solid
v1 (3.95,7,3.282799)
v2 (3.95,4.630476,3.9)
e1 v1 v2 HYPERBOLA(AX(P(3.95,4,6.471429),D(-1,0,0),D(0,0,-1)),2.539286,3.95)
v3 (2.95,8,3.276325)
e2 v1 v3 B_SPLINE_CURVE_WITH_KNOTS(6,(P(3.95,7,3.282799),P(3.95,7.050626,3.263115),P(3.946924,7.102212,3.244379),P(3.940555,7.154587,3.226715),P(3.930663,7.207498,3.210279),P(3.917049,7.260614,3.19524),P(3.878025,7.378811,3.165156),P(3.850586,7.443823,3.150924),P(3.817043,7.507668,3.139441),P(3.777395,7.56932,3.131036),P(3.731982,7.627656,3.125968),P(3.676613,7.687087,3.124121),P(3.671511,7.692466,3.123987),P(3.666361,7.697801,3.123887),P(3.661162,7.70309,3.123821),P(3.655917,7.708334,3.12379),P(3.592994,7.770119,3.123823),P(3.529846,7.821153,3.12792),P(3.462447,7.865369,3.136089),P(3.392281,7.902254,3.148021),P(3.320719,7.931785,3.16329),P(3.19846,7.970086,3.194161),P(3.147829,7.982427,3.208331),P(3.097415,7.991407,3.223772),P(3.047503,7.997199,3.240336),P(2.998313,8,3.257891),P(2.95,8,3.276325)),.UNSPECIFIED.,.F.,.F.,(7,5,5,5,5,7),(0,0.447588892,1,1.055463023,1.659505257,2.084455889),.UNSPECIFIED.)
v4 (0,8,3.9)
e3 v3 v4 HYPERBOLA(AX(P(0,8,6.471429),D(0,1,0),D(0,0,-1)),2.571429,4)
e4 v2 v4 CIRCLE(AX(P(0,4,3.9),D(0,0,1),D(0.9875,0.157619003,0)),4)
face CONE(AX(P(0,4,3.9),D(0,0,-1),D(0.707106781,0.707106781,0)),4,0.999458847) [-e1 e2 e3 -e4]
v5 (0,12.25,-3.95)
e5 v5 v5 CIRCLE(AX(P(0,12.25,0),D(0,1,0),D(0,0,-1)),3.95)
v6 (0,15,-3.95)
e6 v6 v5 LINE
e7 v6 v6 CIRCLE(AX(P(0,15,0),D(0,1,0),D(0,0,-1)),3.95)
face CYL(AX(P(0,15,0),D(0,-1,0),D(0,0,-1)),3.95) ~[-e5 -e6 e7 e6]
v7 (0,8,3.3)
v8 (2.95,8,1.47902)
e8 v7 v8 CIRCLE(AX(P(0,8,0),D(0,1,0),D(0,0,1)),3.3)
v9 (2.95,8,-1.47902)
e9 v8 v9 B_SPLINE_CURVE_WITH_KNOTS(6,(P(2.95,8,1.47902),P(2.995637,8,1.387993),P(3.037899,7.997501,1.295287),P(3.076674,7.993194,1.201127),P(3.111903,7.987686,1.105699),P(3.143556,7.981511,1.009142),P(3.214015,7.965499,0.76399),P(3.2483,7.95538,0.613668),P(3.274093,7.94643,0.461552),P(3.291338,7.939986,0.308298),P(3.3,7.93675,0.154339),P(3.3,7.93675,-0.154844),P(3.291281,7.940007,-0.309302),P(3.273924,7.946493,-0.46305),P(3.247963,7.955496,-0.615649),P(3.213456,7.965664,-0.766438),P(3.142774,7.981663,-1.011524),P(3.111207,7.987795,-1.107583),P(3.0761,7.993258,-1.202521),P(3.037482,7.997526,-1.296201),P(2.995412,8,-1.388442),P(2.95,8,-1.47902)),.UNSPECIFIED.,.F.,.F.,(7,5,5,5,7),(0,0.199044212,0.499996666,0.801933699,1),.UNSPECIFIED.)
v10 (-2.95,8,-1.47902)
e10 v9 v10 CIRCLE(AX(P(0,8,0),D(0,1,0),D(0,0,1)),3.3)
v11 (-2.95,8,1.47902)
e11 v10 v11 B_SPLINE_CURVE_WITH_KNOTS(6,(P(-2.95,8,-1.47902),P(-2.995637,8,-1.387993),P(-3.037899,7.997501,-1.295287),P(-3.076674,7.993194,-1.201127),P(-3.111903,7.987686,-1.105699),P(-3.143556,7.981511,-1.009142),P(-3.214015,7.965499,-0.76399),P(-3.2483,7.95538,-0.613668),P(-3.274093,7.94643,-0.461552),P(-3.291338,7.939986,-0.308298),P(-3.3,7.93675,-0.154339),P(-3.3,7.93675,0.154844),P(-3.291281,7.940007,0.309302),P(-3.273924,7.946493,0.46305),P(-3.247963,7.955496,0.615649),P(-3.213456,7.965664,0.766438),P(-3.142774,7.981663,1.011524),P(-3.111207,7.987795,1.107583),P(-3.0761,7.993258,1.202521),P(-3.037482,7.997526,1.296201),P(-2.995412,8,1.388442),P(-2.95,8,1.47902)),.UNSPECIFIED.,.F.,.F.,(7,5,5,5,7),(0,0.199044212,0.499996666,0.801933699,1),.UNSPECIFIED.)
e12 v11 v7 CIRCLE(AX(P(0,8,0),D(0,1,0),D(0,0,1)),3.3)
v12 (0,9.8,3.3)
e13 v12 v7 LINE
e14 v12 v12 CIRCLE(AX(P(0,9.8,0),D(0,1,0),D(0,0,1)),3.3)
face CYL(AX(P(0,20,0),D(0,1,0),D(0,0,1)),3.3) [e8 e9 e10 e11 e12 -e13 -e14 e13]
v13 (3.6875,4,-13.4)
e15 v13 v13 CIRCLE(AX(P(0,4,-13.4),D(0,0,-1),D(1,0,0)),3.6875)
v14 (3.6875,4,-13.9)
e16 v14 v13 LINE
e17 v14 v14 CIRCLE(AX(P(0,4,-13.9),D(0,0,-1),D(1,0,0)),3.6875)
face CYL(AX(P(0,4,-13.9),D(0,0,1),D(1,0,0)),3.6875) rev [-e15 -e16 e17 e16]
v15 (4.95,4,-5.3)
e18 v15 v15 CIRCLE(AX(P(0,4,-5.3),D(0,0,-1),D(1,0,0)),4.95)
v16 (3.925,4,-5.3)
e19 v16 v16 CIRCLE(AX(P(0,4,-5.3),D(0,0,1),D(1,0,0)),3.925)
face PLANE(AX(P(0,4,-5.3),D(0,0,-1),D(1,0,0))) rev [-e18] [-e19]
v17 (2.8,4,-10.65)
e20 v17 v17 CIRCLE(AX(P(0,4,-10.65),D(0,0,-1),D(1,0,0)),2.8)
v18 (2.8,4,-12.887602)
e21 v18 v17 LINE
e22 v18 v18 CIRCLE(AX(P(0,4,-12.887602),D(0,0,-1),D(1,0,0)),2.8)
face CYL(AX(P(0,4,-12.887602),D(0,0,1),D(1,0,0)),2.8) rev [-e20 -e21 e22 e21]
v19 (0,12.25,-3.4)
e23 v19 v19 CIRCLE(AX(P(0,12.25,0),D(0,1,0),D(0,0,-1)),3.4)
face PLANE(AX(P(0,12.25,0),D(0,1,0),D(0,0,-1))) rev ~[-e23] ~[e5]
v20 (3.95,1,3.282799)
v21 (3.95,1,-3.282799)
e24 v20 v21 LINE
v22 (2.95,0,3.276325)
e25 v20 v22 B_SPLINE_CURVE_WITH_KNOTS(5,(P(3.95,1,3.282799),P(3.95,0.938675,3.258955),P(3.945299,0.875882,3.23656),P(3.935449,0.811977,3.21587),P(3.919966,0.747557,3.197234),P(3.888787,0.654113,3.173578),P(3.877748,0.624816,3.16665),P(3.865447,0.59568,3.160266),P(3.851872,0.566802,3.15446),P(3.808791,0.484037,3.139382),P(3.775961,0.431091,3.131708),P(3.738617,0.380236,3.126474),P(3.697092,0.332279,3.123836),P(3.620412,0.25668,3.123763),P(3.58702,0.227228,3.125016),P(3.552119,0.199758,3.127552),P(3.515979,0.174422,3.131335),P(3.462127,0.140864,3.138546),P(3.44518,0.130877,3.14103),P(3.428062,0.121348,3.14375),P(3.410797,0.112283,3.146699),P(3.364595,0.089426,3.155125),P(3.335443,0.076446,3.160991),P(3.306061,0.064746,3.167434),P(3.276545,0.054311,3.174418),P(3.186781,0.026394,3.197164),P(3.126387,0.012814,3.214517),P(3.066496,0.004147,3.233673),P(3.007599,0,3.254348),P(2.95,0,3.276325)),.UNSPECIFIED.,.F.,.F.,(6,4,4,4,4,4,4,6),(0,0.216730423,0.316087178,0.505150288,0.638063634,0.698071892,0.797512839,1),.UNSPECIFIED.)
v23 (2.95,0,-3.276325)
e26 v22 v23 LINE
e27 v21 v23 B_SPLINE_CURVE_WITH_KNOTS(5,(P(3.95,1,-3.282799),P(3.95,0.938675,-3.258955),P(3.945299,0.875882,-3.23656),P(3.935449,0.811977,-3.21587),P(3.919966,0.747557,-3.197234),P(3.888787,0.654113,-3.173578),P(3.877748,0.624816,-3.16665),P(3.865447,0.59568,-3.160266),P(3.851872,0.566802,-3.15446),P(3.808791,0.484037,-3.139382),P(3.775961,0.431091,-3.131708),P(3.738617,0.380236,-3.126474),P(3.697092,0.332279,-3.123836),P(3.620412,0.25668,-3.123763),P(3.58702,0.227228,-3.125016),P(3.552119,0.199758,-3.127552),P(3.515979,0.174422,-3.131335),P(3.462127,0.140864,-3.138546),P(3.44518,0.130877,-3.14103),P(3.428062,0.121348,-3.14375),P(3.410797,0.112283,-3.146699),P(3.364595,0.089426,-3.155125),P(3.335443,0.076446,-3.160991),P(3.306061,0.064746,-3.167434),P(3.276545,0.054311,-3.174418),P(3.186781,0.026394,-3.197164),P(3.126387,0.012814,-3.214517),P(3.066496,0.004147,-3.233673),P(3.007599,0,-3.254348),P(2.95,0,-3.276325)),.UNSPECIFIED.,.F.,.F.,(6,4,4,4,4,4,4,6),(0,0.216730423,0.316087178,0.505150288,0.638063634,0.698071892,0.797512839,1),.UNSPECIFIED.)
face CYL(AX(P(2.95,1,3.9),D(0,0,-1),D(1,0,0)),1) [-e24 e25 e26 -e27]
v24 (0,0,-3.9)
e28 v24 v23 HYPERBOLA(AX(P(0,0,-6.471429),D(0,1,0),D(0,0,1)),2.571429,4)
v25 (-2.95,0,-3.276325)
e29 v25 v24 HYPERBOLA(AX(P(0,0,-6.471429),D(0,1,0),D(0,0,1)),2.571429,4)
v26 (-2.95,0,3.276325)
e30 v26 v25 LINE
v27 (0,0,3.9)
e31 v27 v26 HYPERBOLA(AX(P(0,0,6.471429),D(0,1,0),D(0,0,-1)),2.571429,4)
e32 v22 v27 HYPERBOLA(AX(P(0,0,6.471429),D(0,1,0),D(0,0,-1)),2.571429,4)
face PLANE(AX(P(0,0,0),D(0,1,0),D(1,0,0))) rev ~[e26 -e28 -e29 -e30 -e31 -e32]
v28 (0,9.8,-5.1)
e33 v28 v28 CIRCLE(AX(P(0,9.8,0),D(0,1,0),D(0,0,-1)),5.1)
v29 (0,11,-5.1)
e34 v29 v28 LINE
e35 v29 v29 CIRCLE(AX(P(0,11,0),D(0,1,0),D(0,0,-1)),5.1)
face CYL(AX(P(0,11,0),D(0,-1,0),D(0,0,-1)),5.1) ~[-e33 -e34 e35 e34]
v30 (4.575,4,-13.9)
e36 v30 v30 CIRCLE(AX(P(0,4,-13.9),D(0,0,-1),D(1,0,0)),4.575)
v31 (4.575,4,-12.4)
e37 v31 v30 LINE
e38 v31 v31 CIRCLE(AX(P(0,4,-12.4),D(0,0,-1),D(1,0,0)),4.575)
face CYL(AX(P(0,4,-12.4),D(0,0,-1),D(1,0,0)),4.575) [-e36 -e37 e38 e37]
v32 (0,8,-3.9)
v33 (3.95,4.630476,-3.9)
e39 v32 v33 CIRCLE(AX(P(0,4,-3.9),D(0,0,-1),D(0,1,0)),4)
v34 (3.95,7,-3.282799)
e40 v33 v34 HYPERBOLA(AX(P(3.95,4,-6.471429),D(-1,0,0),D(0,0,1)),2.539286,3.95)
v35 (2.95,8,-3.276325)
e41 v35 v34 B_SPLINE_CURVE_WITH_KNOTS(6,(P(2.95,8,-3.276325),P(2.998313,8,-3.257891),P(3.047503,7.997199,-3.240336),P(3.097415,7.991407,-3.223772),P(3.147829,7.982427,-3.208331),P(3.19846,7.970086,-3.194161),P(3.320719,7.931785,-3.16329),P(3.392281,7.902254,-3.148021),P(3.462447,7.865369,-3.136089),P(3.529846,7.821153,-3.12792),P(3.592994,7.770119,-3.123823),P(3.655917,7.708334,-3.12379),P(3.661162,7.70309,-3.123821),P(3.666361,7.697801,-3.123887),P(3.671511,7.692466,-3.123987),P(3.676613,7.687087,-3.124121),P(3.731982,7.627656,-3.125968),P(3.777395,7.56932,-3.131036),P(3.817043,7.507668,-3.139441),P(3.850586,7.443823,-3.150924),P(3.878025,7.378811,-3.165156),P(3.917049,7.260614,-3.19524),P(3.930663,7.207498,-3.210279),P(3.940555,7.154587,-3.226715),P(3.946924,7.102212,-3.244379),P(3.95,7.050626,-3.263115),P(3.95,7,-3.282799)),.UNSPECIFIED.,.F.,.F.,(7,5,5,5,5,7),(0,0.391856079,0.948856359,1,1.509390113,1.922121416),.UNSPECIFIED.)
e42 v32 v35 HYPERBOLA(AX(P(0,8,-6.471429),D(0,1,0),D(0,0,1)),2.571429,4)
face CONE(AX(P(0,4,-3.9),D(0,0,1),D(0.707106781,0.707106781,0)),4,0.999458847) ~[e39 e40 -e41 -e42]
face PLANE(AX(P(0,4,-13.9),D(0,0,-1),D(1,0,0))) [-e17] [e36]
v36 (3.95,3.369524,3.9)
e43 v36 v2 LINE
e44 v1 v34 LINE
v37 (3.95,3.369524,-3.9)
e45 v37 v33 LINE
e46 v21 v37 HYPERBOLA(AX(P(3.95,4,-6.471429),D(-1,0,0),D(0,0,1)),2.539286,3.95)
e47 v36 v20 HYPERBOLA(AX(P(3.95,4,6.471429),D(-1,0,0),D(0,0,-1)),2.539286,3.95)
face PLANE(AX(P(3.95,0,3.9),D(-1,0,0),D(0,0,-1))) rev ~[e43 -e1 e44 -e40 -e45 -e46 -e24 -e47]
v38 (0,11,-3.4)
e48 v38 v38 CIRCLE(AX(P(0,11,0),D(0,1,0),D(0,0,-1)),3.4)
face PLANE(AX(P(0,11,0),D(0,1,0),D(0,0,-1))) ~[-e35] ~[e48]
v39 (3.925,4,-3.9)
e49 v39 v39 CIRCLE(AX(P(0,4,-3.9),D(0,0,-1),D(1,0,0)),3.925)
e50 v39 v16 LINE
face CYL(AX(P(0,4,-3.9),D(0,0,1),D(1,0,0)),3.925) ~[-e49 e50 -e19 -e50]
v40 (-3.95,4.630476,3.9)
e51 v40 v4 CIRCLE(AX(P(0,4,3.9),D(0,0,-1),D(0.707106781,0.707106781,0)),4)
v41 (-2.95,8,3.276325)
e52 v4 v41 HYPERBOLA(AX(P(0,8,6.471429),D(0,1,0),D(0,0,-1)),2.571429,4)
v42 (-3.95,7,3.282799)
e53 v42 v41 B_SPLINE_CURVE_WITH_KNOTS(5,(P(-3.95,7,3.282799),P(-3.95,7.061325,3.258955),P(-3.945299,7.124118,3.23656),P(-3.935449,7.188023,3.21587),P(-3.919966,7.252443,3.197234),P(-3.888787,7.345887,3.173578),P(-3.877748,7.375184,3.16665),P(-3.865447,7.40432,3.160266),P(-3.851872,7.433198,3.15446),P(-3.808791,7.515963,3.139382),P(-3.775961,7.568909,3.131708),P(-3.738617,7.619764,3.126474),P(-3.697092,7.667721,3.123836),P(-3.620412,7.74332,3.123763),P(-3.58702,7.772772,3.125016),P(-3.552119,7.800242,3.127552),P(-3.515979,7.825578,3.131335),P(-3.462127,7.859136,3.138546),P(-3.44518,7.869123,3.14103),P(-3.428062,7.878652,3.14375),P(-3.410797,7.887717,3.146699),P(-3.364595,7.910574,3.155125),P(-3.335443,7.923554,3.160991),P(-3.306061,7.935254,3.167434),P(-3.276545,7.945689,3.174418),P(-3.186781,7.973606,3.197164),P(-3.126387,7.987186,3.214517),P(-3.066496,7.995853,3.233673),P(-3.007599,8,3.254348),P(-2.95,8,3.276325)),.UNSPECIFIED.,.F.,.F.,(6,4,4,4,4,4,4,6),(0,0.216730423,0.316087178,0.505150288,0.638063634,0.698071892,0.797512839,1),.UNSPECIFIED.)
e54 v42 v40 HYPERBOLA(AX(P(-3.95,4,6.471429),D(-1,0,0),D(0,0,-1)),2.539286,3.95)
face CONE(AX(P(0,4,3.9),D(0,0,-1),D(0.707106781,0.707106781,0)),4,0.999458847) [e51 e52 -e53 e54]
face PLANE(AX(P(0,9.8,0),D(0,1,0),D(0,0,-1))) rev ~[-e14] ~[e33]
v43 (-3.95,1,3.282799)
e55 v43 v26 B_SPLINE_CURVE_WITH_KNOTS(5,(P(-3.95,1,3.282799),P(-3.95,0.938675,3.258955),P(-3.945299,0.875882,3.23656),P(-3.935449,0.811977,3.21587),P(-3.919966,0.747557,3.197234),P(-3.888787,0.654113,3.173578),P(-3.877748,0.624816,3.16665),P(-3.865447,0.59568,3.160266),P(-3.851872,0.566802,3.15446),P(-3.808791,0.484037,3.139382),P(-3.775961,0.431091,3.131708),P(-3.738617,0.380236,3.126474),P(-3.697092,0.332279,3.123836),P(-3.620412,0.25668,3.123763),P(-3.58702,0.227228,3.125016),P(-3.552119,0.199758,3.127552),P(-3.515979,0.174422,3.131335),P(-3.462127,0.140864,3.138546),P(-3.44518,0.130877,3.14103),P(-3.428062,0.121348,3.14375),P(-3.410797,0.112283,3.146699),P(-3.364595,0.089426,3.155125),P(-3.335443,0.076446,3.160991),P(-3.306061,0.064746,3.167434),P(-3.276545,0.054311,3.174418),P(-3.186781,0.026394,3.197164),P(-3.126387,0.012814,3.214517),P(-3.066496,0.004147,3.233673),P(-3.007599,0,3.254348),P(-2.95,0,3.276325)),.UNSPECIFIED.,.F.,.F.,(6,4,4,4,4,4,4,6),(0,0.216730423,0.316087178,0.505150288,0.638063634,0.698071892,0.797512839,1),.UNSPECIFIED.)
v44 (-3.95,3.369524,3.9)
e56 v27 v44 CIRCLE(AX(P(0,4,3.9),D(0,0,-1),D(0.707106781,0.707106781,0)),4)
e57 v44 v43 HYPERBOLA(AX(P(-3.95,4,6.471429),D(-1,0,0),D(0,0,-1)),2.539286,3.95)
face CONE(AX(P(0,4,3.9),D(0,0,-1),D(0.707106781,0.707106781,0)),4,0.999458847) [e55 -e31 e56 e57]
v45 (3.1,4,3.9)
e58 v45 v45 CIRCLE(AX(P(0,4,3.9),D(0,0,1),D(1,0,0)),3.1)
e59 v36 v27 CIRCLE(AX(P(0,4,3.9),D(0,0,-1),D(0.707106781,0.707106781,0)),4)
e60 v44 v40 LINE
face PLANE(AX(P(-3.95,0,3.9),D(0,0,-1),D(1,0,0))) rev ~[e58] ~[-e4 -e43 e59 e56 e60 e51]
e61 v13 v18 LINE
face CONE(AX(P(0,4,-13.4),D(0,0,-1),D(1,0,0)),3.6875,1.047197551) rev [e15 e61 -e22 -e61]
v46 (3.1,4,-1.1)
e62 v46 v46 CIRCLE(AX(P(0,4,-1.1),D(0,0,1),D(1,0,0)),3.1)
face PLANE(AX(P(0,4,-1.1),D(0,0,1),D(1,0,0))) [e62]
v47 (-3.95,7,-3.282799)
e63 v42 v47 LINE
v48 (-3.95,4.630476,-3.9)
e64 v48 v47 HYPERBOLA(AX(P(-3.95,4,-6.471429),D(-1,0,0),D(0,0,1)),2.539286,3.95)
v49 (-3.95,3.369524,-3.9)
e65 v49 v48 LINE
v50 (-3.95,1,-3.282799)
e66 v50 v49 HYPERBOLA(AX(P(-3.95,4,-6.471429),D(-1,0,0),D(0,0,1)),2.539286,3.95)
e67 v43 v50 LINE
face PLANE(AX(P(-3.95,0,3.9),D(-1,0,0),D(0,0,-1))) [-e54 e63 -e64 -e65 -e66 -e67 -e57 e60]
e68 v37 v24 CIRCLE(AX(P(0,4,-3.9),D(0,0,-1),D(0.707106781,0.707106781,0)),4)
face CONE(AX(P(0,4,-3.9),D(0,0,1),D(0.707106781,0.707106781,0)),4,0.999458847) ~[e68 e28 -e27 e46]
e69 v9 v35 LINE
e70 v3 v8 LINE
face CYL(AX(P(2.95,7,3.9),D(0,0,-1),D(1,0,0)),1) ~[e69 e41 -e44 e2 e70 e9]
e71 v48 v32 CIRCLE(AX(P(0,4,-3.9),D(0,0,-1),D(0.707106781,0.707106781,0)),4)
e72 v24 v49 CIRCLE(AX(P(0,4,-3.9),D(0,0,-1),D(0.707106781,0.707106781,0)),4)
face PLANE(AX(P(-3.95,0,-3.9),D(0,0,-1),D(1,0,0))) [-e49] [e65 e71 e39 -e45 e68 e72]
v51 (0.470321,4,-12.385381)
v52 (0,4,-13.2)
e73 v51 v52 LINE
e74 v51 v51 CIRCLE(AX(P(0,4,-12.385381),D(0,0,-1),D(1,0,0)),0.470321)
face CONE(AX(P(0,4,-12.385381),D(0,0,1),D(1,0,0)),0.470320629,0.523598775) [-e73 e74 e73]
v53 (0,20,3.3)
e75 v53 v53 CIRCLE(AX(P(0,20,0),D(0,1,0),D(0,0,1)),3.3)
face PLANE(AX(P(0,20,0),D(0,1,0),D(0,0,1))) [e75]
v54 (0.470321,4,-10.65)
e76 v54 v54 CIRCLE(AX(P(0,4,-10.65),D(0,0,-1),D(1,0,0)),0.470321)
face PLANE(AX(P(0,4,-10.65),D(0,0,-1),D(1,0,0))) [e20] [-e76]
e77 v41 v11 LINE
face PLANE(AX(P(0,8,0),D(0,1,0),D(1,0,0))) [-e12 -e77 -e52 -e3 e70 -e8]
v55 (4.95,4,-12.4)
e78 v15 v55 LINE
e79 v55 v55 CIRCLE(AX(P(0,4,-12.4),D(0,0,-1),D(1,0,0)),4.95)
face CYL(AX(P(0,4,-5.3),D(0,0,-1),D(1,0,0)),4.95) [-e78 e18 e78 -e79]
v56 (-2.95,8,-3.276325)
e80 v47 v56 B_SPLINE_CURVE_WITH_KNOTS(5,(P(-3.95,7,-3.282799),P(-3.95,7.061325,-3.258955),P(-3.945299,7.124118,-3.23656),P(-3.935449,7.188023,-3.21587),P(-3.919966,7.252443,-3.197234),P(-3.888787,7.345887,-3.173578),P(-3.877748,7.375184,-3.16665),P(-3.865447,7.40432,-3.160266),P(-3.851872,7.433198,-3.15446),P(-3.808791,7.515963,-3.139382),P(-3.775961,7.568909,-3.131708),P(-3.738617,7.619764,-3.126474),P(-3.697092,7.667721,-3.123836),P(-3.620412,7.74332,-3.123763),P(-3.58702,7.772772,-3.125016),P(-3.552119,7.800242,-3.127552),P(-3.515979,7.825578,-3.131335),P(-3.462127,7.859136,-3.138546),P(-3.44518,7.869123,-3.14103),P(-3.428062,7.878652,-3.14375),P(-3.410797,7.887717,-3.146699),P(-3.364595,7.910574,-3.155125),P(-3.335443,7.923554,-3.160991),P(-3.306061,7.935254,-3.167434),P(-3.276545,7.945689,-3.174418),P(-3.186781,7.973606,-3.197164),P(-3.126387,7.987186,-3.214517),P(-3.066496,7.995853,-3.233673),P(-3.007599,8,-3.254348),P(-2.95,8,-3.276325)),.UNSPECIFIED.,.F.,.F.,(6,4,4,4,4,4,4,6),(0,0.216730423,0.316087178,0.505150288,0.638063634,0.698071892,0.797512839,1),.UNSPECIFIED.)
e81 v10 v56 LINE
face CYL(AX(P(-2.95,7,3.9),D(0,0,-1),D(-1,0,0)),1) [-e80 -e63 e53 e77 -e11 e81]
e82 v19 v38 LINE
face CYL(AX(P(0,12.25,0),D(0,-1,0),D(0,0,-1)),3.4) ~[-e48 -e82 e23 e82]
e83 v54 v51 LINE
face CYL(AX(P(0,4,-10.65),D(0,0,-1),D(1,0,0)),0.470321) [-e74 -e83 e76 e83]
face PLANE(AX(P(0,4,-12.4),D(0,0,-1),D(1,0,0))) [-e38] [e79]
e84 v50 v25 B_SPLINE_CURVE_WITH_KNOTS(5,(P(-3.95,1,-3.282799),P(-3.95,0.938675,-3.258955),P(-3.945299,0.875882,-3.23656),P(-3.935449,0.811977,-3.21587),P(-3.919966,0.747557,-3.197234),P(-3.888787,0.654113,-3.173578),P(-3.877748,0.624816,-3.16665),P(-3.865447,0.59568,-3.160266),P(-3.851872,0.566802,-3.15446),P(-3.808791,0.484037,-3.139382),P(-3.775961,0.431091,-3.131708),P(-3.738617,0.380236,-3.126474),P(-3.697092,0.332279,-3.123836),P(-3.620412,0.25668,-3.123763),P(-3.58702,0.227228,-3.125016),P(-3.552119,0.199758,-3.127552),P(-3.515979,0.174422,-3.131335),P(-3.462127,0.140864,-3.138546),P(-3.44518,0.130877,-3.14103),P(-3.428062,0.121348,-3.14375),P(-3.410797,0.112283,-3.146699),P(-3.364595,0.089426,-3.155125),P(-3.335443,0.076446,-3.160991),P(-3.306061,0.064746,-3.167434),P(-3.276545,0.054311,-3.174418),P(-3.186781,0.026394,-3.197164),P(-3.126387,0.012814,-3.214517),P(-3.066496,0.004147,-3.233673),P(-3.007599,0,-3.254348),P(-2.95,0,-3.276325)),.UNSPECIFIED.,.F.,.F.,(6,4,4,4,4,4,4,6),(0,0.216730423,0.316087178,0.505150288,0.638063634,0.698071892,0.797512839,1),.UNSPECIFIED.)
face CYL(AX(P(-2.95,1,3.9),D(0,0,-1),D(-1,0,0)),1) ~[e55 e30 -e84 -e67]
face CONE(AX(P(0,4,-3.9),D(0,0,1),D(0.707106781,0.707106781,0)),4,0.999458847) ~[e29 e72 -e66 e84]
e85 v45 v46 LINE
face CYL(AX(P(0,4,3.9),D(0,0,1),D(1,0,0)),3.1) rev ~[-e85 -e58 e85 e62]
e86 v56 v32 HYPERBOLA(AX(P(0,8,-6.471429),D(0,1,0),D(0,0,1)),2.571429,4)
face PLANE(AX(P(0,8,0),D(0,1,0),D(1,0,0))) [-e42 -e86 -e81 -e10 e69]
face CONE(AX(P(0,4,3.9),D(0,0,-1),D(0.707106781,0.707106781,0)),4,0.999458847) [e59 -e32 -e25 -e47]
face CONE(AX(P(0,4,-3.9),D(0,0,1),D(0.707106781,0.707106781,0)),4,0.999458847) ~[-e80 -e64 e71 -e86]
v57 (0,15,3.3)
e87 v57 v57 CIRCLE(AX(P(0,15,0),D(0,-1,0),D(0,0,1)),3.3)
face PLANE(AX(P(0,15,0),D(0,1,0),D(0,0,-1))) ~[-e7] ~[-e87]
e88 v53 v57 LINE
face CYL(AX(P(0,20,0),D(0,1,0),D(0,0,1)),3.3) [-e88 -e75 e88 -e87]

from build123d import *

# Parameters (mm, degrees)
SKETCH1_W           = 7.9
SKETCH1_H           = 7.8
BOSS_EXTRUDE1_DEPTH = 8
FILLET1_R           = 1
BOSS_EXTRUDE2_REACH = 22.756
SKETCH4_R           = 3.3
SKETCH6_R           = 3.925
BOSS_EXTRUDE3_DEPTH = 6.75
SKETCH9_R           = 3.1
CUT_EXTRUDE1_DEPTH  = 5


with BuildPart() as part:
    # Sketch1 → Boss-Extrude1 (new body)
    with BuildSketch(Plane(origin=(0, 0, 0), x_dir=(1, 0, 0), z_dir=(0, 1, 0))):
        Rectangle(SKETCH1_W, SKETCH1_H)
    extrude(amount=BOSS_EXTRUDE1_DEPTH)

    # Fillet1
    fillet1_edges = [part.edges().sort_by_distance(p)[0] for p in [
        (-3.95, 8, 0),
        (3.95, 8, 0),
        (-3.95, 0, 0),
        (3.95, 0, 0),
    ]]
    fillet(fillet1_edges, radius=FILLET1_R)

    # Sketch3 → Cut-Revolve4 (revolve, cut)
    with BuildSketch(Plane(origin=(-2, 2, 0), x_dir=(0, 0, -1), z_dir=(0.7071067811865462, -0.7071067811865488, 0))):
        Polygon((3, 8.228427125), (4, 8.228427125), (3.9, 6.828427125), align=None)
    cut_revolve4 = revolve(axis=Axis((0, 4, 3.9), (0, 0, -1)), mode=Mode.SUBTRACT)

    # Mirror2: Cut-Revolve4 across plane
    add(cut_revolve4.mirror(Plane.XY), mode=Mode.SUBTRACT)

    # Sketch4 → Boss-Extrude2 (add, up to next)
    with BuildSketch(Plane(origin=(0, 20, 0), x_dir=(1, 0, 0), z_dir=(0, 1, 0)), mode=Mode.PRIVATE) as boss_extrude2_sk1:
        with Locations(Location((0, 0, 0), (0, 0, 270))):
            Circle(SKETCH4_R)
    boss_extrude2_tool1 = extrude(boss_extrude2_sk1.sketch, amount=-BOSS_EXTRUDE2_REACH, mode=Mode.PRIVATE) - part.part
    add(boss_extrude2_tool1.solids().sort_by_distance((0, 20, 0))[0])

    # Sketch5 → Revolve1 (revolve)
    with BuildSketch(Plane(origin=(0, 0, 0), x_dir=(0, 0, -1), z_dir=(1, 0, 0)), mode=Mode.PRIVATE) as revolve1_sk:
        Polygon((-5.1, 11), (-5.1, 9.8), (-3.3, 9.8), (-3.3, 15), (-3.95, 15), (-3.95, 12.25), (-3.4, 12.25), (-3.4, 11), align=None)
    revolve(revolve1_sk.sketch.rotate(Axis((0, -3.247015834, 0), (0, 1, 0)), 180), axis=Axis((0, -3.247015834, 0), (0, 1, 0)))

    # Sketch6 → Boss-Extrude3 (add)
    with BuildSketch(Plane(origin=(0, 0, -3.9), x_dir=(-1, 0, 0), z_dir=(0, 0, -1))):
        with Locations(Location((0, 4, 0), (0, 0, 180))):
            Circle(SKETCH6_R)
    extrude(amount=BOSS_EXTRUDE3_DEPTH)

    # Sketch8 → Revolve2 (revolve)
    with BuildSketch(Plane(origin=(0, 0, 0), x_dir=(0, 0, -1), z_dir=(1, 0, 0)), mode=Mode.PRIVATE) as revolve2_sk:
        Polygon((5.3, 4), (5.3, 8.95), (12.4, 8.95), (12.4, 8.575), (13.9, 8.575), (13.9, 7.6875), (13.4, 7.6875), (12.887601636, 6.8), (10.65, 6.8), (10.65, 4.470320629), (12.385380774, 4.470320629), (13.2, 4), align=None)
    revolve(revolve2_sk.sketch.rotate(Axis((0, 4, 5.444048586), (0, 0, -1)), 90), axis=Axis((0, 4, 5.444048586), (0, 0, -1)))

    # Sketch9 → Cut-Extrude1 (cut)
    with BuildSketch(Plane.XY.offset(3.9)):
        with Locations((0, 4)):
            Circle(SKETCH9_R)
    extrude(amount=-CUT_EXTRUDE1_DEPTH, mode=Mode.SUBTRACT)


solid = part.part
